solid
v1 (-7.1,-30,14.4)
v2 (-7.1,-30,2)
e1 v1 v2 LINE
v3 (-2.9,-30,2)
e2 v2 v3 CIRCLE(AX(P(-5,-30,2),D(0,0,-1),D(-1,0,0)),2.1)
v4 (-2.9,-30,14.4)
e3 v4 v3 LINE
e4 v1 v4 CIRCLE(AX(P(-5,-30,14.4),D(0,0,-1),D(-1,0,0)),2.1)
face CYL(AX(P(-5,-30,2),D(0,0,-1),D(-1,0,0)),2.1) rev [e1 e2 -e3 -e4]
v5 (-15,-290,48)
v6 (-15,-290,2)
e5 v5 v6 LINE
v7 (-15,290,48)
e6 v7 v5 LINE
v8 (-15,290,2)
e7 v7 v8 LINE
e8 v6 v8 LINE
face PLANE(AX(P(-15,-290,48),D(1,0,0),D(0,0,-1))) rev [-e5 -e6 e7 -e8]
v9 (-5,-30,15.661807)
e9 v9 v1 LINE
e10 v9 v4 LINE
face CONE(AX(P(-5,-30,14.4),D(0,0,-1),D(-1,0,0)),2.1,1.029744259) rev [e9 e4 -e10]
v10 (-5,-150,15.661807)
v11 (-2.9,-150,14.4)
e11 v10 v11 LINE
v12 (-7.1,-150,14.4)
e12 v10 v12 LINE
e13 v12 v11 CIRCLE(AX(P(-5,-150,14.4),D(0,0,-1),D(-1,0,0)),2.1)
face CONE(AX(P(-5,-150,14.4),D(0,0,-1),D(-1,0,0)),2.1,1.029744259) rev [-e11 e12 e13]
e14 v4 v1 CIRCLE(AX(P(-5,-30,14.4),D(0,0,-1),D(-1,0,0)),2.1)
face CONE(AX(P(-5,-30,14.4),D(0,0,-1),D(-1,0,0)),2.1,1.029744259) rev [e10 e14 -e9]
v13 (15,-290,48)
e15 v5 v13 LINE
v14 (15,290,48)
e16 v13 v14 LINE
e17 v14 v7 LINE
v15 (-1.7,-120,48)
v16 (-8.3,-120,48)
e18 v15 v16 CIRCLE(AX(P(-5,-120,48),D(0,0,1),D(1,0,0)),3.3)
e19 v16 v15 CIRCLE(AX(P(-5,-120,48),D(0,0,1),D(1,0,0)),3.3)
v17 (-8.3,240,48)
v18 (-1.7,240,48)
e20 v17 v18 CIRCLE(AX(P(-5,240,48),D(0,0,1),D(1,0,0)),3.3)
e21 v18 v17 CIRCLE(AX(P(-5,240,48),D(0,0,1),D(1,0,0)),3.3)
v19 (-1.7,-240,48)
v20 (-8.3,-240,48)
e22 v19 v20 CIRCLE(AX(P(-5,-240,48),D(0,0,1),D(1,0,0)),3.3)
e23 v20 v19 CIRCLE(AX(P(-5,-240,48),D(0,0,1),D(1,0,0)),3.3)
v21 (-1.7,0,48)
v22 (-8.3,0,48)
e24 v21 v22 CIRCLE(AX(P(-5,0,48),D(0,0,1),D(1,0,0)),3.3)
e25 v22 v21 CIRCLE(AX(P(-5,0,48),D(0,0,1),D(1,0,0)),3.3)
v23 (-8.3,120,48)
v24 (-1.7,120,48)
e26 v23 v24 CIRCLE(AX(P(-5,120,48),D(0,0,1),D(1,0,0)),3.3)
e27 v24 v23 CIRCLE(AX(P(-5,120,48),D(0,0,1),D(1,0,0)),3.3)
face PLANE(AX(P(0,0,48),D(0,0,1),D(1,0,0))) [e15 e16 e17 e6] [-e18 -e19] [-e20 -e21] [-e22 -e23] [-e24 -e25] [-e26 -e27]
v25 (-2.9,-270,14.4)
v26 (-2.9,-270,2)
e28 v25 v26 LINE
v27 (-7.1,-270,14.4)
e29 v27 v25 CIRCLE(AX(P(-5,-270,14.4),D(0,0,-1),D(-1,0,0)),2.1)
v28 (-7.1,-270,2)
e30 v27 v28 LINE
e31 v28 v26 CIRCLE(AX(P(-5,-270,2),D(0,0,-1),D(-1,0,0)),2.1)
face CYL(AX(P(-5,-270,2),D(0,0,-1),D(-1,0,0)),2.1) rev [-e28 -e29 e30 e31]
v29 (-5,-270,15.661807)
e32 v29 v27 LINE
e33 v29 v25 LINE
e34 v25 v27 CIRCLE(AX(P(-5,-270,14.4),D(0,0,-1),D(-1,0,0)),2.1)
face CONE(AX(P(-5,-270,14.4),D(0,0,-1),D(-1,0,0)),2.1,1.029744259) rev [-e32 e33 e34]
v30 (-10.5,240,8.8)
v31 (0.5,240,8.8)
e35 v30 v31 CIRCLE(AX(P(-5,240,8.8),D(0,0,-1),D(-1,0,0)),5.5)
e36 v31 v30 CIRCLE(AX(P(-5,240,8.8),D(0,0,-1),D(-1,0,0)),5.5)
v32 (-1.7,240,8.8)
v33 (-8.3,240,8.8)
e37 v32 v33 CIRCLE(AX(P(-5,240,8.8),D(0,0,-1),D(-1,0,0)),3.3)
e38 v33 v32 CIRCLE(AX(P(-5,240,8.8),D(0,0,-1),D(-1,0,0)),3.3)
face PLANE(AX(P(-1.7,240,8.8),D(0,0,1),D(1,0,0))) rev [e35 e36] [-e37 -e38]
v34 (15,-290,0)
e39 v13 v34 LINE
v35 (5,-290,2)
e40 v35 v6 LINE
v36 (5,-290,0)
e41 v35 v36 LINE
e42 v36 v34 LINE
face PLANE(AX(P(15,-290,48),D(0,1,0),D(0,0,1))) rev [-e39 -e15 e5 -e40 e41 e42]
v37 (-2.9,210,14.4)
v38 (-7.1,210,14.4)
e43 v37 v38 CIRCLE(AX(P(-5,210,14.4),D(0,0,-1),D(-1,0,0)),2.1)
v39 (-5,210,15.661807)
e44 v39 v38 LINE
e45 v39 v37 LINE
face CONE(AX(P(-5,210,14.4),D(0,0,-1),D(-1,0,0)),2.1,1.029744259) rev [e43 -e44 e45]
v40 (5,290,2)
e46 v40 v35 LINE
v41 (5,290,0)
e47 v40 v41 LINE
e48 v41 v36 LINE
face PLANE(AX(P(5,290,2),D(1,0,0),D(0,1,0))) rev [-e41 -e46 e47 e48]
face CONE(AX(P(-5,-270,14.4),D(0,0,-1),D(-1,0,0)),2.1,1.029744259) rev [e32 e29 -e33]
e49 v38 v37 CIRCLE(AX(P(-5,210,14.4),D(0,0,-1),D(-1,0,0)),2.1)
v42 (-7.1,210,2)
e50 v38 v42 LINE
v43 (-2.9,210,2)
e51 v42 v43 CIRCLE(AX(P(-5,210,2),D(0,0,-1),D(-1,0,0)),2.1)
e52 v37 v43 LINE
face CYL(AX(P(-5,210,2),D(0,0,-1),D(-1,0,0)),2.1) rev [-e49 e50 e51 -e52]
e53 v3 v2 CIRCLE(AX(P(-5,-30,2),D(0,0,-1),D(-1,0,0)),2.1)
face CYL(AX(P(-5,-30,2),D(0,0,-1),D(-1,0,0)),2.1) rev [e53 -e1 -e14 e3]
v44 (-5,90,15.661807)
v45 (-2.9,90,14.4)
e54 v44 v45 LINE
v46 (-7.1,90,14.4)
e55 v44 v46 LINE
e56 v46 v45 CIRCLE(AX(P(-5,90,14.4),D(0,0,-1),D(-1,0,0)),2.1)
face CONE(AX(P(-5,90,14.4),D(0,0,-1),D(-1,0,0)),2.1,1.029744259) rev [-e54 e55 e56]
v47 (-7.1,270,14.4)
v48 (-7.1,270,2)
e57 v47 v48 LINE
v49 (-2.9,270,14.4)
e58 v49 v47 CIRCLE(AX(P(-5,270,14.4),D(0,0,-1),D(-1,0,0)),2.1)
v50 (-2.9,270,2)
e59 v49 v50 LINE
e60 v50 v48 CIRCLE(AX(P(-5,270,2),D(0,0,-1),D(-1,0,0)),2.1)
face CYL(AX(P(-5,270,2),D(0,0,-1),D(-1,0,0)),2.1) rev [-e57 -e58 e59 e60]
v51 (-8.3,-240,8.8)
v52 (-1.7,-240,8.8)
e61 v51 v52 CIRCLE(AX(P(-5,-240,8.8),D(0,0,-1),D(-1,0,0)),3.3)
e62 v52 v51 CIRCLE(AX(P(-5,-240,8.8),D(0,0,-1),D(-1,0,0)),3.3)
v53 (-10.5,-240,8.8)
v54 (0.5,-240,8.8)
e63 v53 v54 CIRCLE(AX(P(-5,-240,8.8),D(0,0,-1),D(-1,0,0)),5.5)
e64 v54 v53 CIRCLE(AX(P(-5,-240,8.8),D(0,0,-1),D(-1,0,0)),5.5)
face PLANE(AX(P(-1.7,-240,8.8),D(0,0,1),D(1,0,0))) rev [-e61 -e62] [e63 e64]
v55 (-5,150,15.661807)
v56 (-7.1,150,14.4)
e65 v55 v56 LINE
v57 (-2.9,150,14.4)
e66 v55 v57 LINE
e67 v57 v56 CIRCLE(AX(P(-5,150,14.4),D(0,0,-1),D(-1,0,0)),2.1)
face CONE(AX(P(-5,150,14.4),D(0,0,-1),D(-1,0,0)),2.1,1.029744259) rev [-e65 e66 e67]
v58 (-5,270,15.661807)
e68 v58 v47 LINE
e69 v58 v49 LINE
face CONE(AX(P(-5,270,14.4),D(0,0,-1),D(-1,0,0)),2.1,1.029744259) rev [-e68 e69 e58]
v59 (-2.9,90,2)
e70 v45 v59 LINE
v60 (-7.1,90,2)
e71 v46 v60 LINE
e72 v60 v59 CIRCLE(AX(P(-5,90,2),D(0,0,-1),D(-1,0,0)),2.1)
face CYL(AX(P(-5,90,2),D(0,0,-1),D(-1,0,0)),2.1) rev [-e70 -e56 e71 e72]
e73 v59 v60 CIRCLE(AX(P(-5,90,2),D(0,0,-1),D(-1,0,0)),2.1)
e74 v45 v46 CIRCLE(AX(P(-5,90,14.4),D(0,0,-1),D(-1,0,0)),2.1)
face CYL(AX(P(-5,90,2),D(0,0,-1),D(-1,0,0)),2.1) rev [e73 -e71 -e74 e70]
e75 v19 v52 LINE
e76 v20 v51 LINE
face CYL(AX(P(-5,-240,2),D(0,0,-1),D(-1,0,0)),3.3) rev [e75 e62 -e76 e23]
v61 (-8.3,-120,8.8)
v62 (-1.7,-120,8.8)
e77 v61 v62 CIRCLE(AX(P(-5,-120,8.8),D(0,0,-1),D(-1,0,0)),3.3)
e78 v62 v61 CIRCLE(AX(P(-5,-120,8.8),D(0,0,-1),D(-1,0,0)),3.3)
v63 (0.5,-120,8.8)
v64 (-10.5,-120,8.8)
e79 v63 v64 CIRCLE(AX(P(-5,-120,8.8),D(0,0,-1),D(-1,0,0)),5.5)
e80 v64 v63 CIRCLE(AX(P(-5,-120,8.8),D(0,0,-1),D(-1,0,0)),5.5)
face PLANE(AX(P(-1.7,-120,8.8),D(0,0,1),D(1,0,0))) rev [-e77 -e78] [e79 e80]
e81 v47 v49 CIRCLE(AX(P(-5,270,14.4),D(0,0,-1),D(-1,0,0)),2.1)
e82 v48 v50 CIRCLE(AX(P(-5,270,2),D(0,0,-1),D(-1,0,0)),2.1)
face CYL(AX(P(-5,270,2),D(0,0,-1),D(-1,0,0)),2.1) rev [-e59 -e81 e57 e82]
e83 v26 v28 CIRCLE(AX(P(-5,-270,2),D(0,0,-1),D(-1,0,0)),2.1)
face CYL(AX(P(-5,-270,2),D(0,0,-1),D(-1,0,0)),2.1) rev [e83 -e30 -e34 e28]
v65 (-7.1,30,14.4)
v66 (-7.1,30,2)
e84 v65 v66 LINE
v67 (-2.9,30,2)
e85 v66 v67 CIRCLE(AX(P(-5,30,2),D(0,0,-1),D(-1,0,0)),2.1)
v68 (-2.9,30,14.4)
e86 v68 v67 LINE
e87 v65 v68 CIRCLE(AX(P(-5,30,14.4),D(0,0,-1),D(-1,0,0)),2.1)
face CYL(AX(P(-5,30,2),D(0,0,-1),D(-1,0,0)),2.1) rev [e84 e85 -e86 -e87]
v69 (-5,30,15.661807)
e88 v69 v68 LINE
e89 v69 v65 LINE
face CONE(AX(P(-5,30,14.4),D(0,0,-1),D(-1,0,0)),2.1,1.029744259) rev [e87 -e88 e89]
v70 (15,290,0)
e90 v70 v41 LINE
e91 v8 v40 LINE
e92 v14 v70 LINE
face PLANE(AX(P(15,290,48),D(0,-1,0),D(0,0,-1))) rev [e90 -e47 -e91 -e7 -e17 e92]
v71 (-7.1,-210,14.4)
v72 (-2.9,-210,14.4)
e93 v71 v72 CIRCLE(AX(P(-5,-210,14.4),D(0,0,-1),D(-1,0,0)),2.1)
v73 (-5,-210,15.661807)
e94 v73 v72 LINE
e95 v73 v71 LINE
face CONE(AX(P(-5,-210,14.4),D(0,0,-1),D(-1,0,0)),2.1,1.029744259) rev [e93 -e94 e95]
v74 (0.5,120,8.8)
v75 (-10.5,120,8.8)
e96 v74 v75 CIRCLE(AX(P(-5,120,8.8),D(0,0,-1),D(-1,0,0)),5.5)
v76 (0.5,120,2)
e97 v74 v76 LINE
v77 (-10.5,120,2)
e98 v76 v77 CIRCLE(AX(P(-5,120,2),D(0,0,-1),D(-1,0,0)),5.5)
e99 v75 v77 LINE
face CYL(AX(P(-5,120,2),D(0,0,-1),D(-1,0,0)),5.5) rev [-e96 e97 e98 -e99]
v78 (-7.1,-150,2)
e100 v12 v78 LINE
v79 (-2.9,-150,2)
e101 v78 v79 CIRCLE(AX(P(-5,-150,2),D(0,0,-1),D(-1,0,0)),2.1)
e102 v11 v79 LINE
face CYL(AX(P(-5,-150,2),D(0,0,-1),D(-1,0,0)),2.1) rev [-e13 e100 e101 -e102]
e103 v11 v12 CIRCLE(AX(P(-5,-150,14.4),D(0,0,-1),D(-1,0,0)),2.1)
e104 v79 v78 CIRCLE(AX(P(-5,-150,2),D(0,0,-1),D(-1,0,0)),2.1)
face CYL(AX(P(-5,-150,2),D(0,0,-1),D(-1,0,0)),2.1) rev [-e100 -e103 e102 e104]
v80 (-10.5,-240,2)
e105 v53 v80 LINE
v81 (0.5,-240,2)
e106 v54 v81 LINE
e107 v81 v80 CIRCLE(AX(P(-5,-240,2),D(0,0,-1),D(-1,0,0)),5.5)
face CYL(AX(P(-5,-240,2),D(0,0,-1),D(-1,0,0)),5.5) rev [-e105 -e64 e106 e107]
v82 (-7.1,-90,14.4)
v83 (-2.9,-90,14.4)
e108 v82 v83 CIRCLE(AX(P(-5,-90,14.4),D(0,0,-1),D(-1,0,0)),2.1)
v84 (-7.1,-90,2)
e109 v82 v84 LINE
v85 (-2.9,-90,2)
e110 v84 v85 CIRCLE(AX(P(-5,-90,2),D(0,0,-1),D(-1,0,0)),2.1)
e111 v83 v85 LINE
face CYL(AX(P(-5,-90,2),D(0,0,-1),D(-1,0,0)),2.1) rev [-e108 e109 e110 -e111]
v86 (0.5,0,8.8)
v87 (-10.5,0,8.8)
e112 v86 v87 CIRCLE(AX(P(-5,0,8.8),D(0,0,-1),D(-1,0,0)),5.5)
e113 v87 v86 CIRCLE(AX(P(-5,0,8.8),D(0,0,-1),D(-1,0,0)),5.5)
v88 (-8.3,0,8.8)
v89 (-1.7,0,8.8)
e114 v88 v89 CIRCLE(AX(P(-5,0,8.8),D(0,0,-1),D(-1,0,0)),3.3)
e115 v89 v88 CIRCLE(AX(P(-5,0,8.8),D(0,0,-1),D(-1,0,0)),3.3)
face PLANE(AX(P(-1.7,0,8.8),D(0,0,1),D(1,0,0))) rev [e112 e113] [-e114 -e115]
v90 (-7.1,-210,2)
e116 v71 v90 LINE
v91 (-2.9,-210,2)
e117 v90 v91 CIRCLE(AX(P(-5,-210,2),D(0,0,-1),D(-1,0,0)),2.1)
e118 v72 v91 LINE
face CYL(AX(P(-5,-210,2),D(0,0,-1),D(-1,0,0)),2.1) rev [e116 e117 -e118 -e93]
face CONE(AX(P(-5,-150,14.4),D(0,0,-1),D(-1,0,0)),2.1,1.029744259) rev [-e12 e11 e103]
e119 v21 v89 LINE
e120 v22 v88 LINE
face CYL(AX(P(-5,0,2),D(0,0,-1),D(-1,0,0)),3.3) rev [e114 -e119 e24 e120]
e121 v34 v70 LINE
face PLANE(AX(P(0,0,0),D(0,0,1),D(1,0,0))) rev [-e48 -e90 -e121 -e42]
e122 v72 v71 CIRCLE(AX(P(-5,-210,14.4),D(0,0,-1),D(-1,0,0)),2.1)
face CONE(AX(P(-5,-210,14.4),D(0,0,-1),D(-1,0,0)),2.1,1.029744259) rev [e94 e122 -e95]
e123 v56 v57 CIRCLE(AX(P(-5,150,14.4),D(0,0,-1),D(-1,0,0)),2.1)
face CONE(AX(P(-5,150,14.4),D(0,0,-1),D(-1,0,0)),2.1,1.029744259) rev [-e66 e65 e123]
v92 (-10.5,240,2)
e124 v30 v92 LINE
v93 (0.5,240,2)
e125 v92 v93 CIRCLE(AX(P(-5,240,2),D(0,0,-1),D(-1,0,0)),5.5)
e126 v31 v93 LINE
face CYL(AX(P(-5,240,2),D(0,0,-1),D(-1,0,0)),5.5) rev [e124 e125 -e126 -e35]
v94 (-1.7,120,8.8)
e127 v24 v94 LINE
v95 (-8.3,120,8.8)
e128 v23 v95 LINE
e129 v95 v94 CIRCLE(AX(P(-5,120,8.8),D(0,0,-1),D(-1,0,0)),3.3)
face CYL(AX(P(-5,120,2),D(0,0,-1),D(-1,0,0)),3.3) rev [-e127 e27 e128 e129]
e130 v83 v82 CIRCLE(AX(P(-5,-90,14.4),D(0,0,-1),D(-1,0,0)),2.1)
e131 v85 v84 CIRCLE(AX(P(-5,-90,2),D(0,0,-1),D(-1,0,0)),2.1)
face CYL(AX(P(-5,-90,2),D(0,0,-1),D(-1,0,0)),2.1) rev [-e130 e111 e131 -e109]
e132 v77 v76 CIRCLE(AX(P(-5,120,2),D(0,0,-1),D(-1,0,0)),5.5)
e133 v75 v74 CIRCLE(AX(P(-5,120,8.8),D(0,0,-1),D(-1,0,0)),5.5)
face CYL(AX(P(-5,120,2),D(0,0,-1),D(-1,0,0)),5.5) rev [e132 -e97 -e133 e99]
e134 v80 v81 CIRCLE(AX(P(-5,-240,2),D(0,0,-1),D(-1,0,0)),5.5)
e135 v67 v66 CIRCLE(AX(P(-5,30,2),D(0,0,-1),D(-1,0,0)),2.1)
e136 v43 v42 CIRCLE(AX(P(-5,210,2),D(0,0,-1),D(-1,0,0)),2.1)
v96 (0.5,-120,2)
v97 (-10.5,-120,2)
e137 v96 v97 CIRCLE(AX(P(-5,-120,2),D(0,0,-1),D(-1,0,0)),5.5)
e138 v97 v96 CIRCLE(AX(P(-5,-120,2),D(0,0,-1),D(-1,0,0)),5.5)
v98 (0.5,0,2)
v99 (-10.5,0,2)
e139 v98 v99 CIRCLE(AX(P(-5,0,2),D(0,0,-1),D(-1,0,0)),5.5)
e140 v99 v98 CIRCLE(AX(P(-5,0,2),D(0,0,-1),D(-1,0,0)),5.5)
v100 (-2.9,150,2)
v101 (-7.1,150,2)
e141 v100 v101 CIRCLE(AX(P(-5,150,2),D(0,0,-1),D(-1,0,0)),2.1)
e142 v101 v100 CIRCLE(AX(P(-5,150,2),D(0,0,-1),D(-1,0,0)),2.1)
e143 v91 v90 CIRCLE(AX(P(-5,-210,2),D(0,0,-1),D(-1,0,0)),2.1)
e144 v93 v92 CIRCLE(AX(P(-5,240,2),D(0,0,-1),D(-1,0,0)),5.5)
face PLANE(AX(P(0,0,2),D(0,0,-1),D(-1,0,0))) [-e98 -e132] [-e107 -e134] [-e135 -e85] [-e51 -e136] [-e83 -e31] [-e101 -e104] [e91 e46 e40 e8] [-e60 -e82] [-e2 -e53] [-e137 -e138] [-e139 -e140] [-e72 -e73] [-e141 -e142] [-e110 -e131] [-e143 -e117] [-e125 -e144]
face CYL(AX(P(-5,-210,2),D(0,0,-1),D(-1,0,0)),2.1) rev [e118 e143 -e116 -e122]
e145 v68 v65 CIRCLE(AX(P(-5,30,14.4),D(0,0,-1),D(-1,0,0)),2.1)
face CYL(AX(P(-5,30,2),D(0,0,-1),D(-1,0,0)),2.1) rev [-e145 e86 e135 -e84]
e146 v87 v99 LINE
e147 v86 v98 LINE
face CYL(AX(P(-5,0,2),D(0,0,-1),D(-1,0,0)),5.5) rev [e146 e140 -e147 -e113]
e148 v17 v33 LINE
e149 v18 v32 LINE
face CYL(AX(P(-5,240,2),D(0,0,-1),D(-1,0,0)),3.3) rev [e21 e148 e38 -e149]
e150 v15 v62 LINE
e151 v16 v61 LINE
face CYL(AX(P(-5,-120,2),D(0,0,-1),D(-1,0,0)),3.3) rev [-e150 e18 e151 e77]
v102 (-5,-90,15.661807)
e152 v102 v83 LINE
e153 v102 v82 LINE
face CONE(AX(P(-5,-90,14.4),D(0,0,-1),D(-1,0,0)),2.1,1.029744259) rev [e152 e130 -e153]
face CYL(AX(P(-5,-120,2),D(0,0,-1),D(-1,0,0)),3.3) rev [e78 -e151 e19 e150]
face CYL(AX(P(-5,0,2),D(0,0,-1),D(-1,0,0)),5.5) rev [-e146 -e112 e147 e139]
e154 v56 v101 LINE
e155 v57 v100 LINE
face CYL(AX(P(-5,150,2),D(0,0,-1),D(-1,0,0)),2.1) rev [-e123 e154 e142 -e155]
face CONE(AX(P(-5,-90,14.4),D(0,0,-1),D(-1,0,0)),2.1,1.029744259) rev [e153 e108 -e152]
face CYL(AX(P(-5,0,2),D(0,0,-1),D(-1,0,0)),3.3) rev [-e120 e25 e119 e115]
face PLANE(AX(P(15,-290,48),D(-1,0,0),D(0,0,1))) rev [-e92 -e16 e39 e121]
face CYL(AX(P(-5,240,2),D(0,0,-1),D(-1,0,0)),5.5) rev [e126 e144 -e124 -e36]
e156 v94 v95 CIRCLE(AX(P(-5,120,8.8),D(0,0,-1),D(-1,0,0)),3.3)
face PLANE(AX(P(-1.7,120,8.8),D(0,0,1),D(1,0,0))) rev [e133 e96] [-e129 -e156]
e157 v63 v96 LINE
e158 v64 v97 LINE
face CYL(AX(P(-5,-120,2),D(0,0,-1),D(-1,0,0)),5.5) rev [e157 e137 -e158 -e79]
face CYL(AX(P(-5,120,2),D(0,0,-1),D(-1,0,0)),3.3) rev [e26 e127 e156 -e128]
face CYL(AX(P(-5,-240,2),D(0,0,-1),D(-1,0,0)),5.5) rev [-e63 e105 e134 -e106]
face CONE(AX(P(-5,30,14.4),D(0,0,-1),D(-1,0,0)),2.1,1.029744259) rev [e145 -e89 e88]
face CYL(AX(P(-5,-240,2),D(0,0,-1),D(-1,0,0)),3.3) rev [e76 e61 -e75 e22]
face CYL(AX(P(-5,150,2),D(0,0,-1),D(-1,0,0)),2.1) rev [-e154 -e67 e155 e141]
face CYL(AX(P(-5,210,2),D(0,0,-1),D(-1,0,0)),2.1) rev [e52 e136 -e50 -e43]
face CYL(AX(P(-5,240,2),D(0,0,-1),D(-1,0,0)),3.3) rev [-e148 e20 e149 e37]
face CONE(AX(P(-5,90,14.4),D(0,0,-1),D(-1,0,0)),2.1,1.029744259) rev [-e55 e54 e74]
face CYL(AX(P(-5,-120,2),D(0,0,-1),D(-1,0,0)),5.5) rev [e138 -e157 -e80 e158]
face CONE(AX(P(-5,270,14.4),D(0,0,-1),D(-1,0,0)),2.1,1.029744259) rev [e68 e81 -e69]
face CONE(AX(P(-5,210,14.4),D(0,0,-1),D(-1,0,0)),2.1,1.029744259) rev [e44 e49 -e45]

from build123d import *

# Parameters (mm, degrees)
SKETCH_1_W                = 30
SKETCH_1_H                = 580
EXTRUDE_1_DEPTH           = 48
SKETCH_2_W                = 20
SKETCH_2_H                = 580
CUT_EXTRUDE_1_DEPTH       = 2
PATTERN_LINEAR_1_COUNT    = 10
PATTERN_LINEAR_1_PITCH    = 60
HOLE_WIZARD_1_D           = 6.6
HOLE_WIZARD_1_CBORE_D     = 11
HOLE_WIZARD_1_CBORE_DEPTH = 6.8
PATTERN_LINEAR_2_COUNT    = 5
PATTERN_LINEAR_2_PITCH    = 120


with BuildPart() as part:
    # 草图1 → 凸台-拉伸1 (new body)
    with BuildSketch(Plane.XY):
        Rectangle(SKETCH_1_W, SKETCH_1_H)
    extrude(amount=EXTRUDE_1_DEPTH)

    # 草图2 → 切除-拉伸1 (cut)
    with BuildSketch(Plane(origin=(0, 0, 0), x_dir=(-1, 0, 0), z_dir=(0, 0, -1))):
        with Locations((5, 0)):
            Rectangle(SKETCH_2_W, SKETCH_2_H)
    extrude(amount=-CUT_EXTRUDE_1_DEPTH, mode=Mode.SUBTRACT)

    # 草图4 → M5 螺纹孔1 (revolve, cut)
    with BuildSketch(Plane(origin=(-5, 270, 2), x_dir=(0, 1, 0), z_dir=(1, 0, 0))):
        Polygon((0, 0), (0, 13.6618073), (2.1, 12.4), (2.1, 0), align=None)
    hole_wizard_m5_1 = revolve(axis=Axis((-5, 270, -4.35), (0, 0, 1)), mode=Mode.SUBTRACT)

    # 阵列(线性)1: M5 螺纹孔1 ×10
    with Locations(*[(0, -i * PATTERN_LINEAR_1_PITCH, 0) for i in range(1, PATTERN_LINEAR_1_COUNT)]):
        add(hole_wizard_m5_1, mode=Mode.SUBTRACT)

    # 打孔尺寸(%根据)内六角圆柱头螺钉的类型1 (through all)
    with Locations(Plane(origin=(0, 0, 2), x_dir=(-1, 0, 0), z_dir=(0, 0, -1))):
        with Locations((5, 240)):
            hole_wizard_1 = CounterBoreHole(HOLE_WIZARD_1_D / 2, HOLE_WIZARD_1_CBORE_D / 2, HOLE_WIZARD_1_CBORE_DEPTH)

    # 阵列(线性)2: 打孔尺寸(%根据)内六角圆柱头螺钉的类型1 ×5
    with Locations(*[(0, -i * PATTERN_LINEAR_2_PITCH, 0) for i in range(1, PATTERN_LINEAR_2_COUNT)]):
        add(hole_wizard_1, mode=Mode.SUBTRACT)


solid = part.part
